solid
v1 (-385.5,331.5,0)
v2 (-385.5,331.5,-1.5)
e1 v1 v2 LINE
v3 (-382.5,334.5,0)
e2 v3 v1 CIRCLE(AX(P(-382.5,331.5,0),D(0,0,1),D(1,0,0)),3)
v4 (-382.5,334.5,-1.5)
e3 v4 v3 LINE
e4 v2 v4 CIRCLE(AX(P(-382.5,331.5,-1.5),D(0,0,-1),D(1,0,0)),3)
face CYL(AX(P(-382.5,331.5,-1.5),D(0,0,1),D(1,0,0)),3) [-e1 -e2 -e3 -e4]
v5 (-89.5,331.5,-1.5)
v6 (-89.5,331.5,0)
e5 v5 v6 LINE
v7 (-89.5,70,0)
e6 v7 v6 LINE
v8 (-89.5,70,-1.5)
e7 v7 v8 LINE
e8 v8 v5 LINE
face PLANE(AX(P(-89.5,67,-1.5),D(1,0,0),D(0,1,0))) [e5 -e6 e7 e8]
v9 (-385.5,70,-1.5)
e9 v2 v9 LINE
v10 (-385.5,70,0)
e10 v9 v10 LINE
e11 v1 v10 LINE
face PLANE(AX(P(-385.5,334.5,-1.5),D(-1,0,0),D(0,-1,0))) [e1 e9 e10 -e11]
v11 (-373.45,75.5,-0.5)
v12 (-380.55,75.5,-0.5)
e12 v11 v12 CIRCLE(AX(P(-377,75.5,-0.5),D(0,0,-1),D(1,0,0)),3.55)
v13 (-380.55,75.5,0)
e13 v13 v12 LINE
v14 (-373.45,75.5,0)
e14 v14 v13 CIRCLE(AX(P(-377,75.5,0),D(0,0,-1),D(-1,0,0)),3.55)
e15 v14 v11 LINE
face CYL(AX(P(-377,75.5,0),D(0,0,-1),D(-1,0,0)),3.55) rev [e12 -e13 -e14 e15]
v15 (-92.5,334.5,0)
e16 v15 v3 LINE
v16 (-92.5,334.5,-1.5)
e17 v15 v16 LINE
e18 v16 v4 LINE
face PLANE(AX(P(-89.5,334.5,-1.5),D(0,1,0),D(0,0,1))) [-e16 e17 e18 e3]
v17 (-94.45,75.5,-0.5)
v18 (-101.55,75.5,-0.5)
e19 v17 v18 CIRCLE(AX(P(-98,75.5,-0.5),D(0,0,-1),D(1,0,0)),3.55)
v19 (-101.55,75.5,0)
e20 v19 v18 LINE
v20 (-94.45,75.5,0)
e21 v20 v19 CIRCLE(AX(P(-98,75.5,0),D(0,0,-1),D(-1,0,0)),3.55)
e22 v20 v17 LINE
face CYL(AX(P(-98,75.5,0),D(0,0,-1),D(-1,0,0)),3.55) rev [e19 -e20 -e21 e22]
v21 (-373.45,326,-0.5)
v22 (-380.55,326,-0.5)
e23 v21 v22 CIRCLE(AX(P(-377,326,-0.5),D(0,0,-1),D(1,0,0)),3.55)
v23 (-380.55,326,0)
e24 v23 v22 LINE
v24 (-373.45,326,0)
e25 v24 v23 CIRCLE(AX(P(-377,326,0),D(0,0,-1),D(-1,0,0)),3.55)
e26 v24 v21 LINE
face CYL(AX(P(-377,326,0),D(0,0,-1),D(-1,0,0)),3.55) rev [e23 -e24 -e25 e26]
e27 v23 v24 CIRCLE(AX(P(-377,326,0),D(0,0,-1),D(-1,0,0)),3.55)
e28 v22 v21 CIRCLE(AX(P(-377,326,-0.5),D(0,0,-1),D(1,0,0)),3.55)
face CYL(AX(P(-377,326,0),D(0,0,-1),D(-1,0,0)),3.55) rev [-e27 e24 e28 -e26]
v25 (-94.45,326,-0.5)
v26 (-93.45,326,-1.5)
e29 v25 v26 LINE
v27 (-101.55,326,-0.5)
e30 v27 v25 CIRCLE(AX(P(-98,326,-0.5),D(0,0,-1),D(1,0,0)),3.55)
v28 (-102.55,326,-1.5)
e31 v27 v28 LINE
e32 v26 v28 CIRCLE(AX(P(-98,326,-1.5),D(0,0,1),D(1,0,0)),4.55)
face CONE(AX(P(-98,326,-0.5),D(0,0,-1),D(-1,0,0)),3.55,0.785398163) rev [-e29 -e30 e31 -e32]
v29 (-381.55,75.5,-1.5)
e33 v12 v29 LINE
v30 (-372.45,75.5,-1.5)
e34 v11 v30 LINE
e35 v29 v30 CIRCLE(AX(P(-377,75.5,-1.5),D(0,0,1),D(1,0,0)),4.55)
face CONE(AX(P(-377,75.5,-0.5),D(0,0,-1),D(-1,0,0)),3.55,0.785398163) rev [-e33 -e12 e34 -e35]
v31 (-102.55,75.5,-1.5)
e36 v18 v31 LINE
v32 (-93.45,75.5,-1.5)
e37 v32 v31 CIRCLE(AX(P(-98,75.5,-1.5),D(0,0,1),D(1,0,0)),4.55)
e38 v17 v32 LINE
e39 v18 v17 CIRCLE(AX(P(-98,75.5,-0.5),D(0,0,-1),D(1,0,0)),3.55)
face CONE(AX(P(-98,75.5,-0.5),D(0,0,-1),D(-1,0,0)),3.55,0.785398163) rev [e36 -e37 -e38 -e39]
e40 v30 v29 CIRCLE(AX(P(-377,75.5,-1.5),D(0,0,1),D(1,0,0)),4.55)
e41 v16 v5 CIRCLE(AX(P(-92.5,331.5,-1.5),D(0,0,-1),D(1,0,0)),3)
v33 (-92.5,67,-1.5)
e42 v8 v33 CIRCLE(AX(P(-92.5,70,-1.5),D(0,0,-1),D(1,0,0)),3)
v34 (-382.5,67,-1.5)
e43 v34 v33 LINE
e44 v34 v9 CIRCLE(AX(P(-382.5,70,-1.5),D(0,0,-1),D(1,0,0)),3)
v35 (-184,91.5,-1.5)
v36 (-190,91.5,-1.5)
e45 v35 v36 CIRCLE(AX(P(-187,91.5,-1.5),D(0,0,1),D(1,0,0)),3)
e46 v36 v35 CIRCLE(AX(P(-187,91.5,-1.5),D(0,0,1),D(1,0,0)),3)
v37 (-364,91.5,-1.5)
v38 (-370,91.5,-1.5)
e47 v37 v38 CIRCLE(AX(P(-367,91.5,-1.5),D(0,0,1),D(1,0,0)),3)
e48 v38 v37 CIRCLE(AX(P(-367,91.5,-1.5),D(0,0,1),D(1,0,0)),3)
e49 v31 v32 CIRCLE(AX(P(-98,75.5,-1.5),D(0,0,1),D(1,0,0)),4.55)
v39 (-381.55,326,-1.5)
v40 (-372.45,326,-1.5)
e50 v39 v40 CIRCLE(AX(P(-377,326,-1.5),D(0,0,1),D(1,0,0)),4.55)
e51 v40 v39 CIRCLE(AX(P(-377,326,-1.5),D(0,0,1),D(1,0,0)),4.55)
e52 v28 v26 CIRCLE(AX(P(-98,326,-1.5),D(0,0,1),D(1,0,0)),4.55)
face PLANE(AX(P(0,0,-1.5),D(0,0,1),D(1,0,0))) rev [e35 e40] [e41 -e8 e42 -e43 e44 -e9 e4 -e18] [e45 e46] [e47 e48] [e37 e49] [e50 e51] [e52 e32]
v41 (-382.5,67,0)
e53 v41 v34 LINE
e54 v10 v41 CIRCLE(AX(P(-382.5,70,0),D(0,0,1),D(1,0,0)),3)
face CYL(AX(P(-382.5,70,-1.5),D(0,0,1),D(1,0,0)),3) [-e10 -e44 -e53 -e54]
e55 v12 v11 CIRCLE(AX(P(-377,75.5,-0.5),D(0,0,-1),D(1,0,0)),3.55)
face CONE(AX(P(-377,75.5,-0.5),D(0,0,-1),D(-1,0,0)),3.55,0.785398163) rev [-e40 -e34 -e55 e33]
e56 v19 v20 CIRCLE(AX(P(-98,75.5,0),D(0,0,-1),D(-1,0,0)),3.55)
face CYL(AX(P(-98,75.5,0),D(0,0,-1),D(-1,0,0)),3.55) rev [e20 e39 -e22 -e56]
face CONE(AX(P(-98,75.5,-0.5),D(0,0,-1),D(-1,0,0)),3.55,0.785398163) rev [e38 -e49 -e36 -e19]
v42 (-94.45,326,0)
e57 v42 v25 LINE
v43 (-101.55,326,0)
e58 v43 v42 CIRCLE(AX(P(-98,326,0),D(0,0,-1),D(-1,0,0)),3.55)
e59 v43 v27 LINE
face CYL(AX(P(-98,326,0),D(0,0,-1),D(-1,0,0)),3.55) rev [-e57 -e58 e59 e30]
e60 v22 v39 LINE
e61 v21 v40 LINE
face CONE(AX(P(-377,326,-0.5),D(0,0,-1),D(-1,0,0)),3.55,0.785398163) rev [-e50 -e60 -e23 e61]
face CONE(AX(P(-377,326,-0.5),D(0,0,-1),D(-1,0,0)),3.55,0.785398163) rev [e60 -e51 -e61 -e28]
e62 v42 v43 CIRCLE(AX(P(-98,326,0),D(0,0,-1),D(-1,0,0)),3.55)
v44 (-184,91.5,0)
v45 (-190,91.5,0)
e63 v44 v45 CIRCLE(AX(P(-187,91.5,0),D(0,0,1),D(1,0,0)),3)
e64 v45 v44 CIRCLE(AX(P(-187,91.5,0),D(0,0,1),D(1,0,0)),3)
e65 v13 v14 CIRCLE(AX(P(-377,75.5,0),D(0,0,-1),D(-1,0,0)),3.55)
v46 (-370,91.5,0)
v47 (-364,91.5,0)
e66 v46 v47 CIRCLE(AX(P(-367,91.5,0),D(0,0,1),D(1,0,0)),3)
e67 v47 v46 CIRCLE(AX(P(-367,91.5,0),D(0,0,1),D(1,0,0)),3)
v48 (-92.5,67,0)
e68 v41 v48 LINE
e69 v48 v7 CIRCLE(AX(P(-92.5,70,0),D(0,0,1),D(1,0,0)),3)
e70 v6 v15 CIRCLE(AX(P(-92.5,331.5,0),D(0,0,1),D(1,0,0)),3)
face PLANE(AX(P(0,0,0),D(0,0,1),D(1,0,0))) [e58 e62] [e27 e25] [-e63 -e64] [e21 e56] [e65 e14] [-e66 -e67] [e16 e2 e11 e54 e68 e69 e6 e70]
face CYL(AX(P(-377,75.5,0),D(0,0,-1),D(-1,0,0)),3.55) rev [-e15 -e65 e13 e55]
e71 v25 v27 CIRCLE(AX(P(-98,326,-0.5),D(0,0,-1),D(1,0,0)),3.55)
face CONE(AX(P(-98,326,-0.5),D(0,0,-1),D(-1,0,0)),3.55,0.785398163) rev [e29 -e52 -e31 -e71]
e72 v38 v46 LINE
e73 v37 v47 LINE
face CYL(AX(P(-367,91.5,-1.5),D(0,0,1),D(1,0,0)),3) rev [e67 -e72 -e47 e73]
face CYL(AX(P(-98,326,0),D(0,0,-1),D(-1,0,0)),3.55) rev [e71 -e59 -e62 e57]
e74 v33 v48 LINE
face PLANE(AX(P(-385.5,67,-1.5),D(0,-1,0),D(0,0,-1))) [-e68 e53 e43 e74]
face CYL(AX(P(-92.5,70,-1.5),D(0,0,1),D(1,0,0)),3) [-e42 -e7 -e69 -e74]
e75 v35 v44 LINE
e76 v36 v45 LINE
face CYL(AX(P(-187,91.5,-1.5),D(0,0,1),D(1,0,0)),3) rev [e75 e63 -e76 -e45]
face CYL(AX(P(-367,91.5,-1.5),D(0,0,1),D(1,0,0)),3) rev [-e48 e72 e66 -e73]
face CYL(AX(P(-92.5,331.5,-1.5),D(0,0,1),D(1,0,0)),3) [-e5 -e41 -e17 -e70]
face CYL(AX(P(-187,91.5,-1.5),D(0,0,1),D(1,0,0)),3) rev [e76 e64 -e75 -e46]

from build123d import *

# Parameters (mm, degrees)
SKETCH_1_W          = 296
SKETCH_1_H          = 267.5
EXTRUDE_1_DEPTH     = 1.5
FILLET_1_R          = 3
SKETCH_6_R          = 3
CUT_EXTRUDE_1_DEPTH = 1.5
SKETCH_7_R          = 3.55
CUT_EXTRUDE_2_DEPTH = 1.5
CHAMFER_1_SIZE      = 1


with BuildPart() as part:
    # 草图1 → 凸台-拉伸1 (new body)
    with BuildSketch(Plane.XY):
        with Locations((-237.5, 200.75)):
            Rectangle(SKETCH_1_W, SKETCH_1_H)
    extrude(amount=-EXTRUDE_1_DEPTH)

    # 圆角1
    fillet_1_edges = [part.edges().sort_by_distance(p)[0] for p in [
        (-385.5, 67, -0.75),
        (-385.5, 334.5, -0.75),
        (-89.5, 334.5, -0.75),
        (-89.5, 67, -0.75),
    ]]
    fillet(fillet_1_edges, radius=FILLET_1_R)

    # 草图6 → 切除-拉伸1 (cut)
    with BuildSketch(Plane.XY):
        with Locations((-367, 91.5)):
            Circle(SKETCH_6_R)
        with Locations((-187, 91.5)):
            Circle(SKETCH_6_R)
    extrude(amount=-CUT_EXTRUDE_1_DEPTH, mode=Mode.SUBTRACT)

    # 草图7 → 切除-拉伸2 (cut)
    with BuildSketch(Plane(origin=(0, 0, -1.5), x_dir=(-1, 0, 0), z_dir=(0, 0, -1))):
        with Locations((98, 326)):
            Circle(SKETCH_7_R)
        with Locations((377, 326)):
            Circle(SKETCH_7_R)
        with Locations((377, 75.5)):
            Circle(SKETCH_7_R)
        with Locations((98, 75.5)):
            Circle(SKETCH_7_R)
    extrude(amount=-CUT_EXTRUDE_2_DEPTH, mode=Mode.SUBTRACT)

    # 倒角1
    chamfer_1_edges = [part.edges().sort_by_distance(p)[0] for p in [
        (-94.45, 326, -1.5),
        (-373.45, 326, -1.5),
        (-373.45, 75.5, -1.5),
        (-94.45, 75.5, -1.5),
    ]]
    chamfer(chamfer_1_edges, length=CHAMFER_1_SIZE)


solid = part.part
